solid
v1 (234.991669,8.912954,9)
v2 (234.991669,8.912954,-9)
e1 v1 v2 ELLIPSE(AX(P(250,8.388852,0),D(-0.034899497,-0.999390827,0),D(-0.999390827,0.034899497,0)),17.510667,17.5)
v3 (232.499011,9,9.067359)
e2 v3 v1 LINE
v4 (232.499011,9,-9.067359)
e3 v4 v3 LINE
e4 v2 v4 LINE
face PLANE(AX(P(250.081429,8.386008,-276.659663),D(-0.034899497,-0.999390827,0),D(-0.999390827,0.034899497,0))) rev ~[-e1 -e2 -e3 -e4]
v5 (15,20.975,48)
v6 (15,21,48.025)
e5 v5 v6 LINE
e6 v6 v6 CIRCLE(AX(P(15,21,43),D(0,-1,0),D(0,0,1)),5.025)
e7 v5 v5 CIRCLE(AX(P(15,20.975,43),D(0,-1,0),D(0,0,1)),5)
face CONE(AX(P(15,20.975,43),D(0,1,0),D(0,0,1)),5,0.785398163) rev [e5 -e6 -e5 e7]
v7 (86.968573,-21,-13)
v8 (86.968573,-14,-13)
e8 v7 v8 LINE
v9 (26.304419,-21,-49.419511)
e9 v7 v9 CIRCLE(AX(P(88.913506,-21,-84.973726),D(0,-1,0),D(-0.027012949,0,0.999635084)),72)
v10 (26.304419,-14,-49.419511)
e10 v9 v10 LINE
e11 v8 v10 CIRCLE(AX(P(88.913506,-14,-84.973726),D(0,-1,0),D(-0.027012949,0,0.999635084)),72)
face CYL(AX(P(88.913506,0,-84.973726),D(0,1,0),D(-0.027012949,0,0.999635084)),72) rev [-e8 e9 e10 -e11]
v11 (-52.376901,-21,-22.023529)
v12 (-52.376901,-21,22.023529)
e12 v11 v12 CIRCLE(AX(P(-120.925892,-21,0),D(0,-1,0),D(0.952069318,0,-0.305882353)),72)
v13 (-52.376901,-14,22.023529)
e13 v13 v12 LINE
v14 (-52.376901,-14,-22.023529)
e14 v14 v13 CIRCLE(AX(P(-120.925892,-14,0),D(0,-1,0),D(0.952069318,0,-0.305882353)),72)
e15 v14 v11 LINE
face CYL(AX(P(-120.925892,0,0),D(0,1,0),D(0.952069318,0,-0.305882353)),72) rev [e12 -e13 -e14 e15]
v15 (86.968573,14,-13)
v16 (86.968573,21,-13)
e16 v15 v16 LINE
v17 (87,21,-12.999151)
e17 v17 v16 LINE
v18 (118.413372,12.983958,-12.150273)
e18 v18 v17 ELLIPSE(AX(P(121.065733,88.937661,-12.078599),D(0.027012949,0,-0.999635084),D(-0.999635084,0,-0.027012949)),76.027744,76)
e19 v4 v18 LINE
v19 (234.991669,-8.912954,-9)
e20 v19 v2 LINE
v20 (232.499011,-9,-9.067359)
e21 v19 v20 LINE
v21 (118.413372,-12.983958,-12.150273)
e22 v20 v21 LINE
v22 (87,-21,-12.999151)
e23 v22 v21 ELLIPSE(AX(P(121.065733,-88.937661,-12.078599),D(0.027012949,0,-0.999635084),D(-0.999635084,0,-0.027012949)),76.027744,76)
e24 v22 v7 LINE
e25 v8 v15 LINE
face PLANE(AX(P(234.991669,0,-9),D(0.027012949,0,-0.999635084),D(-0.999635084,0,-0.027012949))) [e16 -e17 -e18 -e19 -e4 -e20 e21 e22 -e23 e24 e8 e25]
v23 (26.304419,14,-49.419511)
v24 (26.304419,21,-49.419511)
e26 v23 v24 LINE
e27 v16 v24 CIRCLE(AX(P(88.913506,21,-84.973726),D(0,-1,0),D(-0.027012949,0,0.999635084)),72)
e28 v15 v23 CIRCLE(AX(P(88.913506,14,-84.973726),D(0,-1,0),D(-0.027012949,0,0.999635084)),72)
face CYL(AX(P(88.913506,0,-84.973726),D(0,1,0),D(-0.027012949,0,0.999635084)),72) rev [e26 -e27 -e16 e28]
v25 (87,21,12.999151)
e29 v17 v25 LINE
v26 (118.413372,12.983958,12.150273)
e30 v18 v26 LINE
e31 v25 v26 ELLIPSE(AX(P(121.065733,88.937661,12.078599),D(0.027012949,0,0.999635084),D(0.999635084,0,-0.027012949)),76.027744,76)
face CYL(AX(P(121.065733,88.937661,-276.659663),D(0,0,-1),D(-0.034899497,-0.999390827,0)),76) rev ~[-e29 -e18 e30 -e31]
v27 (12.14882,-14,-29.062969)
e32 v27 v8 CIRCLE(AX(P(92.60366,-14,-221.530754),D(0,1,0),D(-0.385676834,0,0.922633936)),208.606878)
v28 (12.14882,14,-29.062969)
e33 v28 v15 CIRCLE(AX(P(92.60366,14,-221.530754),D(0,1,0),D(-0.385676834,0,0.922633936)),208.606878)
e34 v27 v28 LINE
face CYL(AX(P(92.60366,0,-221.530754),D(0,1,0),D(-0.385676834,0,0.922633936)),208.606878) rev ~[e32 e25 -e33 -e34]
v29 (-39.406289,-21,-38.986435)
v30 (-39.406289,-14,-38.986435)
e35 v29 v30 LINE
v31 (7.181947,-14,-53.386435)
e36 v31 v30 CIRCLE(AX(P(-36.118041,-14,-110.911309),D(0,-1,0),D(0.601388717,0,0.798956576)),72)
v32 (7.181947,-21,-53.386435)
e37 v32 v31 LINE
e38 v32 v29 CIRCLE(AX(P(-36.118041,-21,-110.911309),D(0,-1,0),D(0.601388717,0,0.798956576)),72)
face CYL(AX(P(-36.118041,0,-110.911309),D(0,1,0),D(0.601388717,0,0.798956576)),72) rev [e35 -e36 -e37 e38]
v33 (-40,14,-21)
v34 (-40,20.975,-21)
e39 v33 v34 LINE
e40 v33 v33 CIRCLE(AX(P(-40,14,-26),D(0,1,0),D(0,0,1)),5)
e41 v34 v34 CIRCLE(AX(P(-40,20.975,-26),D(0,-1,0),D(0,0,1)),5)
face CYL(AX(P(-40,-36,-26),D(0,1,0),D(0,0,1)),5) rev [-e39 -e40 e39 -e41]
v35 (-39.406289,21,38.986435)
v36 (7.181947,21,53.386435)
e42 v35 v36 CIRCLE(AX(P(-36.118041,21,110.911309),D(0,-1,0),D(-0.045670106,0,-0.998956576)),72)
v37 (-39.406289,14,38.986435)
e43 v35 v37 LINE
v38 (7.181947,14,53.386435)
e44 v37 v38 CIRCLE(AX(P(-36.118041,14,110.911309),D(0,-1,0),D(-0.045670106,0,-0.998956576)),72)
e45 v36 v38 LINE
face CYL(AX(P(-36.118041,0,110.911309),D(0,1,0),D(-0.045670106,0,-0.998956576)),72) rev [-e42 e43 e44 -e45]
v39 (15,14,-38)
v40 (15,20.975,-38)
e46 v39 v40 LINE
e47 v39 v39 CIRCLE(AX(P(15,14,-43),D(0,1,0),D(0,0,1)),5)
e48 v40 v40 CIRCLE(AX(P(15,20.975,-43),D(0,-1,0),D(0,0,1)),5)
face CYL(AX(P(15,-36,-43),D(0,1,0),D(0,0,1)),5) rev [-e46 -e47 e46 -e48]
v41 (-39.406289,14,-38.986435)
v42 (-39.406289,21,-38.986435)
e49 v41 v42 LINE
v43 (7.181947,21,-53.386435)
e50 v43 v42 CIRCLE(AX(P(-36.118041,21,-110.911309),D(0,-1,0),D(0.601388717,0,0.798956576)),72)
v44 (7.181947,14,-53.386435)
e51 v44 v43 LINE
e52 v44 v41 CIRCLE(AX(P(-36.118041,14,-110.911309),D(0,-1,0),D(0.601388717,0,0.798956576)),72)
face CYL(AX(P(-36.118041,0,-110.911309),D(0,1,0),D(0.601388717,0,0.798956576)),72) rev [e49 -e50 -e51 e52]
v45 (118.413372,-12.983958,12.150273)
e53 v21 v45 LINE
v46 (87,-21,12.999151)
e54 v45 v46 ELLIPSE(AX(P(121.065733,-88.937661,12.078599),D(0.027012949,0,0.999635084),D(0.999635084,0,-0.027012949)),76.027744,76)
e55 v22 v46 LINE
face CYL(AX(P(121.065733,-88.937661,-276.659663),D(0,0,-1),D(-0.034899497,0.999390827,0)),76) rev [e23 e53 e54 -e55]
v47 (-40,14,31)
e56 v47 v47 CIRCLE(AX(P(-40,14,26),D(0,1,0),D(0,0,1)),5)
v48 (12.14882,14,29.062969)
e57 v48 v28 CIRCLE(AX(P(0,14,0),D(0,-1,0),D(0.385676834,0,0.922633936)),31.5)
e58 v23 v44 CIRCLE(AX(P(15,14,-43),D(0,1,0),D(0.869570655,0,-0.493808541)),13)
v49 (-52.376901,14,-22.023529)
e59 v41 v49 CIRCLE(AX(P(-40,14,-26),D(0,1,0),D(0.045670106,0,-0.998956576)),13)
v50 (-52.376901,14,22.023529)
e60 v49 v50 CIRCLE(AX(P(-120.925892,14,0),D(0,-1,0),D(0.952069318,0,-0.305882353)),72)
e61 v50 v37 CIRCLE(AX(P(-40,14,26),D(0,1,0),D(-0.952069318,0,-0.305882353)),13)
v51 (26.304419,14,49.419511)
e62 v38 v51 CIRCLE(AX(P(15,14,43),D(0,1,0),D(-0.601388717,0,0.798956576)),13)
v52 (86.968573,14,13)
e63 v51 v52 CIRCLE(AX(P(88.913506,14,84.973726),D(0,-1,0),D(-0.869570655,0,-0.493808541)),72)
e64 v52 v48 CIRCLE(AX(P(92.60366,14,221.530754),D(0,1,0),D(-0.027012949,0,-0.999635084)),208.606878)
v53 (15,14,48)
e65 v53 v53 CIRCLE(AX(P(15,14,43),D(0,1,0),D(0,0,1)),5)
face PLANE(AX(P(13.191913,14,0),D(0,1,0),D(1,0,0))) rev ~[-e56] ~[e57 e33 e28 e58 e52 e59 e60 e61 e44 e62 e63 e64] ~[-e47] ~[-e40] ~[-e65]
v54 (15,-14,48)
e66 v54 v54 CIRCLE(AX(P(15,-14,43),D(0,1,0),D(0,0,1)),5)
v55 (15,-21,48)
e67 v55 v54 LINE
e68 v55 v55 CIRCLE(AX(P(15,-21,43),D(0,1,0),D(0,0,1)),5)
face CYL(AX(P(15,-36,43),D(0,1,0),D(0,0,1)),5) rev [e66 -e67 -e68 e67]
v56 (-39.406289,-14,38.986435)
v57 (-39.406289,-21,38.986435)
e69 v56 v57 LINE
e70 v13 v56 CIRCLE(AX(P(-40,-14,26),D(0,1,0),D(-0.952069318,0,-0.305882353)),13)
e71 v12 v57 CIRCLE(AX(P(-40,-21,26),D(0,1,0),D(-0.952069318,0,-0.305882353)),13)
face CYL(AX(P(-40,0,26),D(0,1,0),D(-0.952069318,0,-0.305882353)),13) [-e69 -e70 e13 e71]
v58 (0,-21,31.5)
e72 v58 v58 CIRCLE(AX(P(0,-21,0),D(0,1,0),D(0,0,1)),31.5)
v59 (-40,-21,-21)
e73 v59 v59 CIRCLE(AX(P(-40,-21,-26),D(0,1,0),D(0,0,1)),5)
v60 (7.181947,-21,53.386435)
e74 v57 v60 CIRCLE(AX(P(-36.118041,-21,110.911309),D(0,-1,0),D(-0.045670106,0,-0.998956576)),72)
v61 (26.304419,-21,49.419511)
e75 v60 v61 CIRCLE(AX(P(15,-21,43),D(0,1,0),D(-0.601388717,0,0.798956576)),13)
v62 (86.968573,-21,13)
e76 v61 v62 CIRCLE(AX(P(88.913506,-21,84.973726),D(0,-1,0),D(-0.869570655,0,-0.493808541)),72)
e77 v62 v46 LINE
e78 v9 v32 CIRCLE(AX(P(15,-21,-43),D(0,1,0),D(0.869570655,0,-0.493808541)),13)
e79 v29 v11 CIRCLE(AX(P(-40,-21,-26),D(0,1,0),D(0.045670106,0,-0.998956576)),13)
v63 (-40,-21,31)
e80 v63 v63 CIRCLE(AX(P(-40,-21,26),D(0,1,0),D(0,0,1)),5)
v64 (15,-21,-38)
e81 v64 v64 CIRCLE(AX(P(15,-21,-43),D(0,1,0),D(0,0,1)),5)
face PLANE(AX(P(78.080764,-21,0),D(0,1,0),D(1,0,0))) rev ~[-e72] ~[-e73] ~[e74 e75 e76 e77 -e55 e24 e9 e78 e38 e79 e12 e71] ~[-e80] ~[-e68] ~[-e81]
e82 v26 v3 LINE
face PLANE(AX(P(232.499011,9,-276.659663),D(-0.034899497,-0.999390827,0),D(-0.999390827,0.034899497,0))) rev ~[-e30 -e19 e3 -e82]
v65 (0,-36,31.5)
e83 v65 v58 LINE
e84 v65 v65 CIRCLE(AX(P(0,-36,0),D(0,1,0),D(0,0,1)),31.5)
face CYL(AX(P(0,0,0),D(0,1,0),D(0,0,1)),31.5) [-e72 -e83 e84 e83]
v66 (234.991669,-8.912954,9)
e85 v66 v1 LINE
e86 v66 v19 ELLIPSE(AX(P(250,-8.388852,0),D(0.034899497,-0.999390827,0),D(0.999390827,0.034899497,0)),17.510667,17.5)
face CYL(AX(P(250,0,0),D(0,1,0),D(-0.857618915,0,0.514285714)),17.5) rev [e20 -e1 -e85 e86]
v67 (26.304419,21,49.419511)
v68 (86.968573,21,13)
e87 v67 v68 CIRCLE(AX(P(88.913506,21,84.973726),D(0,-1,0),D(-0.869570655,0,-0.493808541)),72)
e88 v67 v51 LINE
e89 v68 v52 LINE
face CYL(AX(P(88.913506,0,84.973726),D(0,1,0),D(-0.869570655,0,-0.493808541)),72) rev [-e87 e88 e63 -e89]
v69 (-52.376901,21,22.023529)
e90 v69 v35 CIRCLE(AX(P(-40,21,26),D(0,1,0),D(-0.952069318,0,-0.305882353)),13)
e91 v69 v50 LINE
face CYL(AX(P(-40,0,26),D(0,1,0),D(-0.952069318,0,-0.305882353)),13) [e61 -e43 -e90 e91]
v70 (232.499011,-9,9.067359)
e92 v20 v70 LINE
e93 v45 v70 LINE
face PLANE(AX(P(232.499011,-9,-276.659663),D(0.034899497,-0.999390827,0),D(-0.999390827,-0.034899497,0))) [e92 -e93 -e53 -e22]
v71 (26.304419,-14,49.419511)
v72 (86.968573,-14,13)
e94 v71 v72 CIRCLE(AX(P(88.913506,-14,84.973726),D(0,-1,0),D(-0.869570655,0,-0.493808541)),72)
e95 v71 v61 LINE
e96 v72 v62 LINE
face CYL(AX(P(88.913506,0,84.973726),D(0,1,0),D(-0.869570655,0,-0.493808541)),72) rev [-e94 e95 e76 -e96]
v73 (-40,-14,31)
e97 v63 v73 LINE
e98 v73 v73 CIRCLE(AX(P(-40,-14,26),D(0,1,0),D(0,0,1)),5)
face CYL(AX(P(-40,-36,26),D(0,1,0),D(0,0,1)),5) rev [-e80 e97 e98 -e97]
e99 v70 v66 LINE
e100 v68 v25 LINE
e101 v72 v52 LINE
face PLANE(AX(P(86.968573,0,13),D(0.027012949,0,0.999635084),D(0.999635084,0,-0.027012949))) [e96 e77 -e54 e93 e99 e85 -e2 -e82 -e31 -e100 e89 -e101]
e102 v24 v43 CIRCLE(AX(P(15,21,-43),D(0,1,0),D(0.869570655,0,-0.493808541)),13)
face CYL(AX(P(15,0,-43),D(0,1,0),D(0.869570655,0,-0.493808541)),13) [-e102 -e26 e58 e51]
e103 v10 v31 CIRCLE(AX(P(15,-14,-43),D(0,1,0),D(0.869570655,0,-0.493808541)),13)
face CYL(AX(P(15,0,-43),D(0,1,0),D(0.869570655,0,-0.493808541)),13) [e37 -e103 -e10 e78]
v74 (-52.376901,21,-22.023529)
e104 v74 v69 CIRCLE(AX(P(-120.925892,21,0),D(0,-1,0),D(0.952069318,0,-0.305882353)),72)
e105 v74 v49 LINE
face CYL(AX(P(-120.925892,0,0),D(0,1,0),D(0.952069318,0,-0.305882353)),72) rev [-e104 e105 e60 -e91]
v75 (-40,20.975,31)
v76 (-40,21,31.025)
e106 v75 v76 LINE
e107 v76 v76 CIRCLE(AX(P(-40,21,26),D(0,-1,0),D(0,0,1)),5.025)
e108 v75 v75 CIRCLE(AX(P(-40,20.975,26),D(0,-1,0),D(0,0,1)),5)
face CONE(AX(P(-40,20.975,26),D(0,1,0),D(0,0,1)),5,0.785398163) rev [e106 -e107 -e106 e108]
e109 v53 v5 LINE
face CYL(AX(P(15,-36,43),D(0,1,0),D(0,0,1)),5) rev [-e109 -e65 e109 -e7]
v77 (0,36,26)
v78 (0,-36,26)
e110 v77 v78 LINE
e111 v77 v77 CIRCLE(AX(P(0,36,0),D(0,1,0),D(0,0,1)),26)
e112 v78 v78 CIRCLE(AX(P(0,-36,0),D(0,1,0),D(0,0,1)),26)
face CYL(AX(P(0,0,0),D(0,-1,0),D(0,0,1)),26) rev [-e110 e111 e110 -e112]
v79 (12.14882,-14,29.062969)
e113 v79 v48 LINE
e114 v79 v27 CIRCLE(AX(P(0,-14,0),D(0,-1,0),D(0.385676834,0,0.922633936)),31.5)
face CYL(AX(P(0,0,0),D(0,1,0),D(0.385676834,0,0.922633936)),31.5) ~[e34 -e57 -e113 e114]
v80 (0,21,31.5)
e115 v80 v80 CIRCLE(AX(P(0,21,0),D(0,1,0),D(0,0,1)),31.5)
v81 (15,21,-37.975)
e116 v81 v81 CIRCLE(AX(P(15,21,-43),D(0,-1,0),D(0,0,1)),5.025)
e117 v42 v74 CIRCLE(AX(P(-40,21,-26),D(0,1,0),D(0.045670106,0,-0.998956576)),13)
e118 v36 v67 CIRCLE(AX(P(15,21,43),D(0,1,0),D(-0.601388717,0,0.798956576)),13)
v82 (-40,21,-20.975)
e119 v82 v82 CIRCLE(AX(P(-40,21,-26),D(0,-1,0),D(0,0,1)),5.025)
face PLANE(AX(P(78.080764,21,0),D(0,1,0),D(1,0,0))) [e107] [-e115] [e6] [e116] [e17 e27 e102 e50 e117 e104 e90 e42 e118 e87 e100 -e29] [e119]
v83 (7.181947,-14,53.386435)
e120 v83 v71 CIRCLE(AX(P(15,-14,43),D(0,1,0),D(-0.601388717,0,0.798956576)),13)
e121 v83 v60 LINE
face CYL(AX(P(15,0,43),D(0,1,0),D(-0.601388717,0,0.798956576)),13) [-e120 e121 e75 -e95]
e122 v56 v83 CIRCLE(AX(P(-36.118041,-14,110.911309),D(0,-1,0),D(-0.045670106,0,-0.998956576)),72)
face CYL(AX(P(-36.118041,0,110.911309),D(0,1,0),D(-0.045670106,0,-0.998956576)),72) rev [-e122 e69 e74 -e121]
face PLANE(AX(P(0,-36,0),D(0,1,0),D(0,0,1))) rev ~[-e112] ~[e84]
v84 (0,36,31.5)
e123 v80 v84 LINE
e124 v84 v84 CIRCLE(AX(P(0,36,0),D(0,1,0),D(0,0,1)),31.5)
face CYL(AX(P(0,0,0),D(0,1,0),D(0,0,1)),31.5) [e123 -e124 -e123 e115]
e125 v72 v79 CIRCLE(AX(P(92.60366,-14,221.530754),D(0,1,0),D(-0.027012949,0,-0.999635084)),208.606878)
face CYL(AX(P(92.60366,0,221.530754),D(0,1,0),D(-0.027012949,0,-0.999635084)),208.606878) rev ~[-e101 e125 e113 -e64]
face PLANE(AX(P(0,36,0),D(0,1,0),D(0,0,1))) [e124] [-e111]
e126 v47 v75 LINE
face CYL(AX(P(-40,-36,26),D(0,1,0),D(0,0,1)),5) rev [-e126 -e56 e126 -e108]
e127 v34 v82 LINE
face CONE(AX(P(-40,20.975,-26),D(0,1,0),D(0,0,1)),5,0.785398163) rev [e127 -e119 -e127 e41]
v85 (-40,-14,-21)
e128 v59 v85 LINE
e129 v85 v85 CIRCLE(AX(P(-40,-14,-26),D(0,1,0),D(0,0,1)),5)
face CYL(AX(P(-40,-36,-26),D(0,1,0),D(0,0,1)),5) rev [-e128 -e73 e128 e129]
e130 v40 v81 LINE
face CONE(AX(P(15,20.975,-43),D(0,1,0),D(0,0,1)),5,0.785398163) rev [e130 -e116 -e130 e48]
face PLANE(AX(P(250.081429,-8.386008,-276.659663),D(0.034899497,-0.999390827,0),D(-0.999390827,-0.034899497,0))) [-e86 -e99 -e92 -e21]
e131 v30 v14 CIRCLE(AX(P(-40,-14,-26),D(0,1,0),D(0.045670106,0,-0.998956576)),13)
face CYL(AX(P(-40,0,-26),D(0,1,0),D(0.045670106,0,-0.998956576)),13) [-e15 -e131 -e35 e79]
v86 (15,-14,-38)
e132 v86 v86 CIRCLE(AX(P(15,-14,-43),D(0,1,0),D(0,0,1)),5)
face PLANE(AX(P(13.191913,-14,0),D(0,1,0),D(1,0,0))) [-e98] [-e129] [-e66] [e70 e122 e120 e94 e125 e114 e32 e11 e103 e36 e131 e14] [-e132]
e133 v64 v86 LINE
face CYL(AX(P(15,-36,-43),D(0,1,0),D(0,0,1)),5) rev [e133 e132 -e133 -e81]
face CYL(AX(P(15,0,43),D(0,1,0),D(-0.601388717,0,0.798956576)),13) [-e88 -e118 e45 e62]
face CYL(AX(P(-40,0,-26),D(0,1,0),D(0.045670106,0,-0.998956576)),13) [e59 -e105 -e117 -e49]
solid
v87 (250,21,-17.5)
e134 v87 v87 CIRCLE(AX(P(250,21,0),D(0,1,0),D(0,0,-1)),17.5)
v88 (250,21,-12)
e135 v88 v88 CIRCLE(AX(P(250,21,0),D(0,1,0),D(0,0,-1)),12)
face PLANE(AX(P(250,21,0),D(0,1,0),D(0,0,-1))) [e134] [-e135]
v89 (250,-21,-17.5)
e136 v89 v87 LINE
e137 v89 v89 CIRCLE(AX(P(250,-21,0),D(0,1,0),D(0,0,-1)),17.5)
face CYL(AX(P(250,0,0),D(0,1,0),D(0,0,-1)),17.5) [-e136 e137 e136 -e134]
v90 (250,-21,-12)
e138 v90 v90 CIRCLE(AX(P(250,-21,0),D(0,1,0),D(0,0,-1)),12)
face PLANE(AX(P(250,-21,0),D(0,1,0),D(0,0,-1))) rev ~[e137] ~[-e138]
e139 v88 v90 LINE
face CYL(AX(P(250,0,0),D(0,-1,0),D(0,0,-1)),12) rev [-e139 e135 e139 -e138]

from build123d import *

# Parameters (mm, degrees)
ROD_PROFILE_SKETCH_R       = 31.5
ROD_PROFILE_SKETCH_R_2     = 26
ROD_BODY_DEPTH             = 36
SKETCH2_7_R                = 31.5
BIG_END_BOSS_DEPTH         = 21
SKETCH2_8_R                = 17.5
SKETCH2_8_R_2              = 12
SMALL_END_BOSS_DEPTH       = 21
BIG_END_CUT_DEPTH          = 14
BOLT_HOLES_10_AT_2_COUNT   = 2
BOLT_HOLES_10_AT_2_PITCH   = 57.567351858
BOLT_HOLES_10_AT_3_COUNT   = 2
BOLT_HOLES_10_AT_3_PITCH   = 86
BOLT_HOLES_10_AT_4_COUNT   = 2
BOLT_HOLES_10_AT_4_PITCH   = 88.238313674
SHANK_TAPER_CUT_DEPTH      = 276.659663353
SHANK_TAPER_CUT_DEPTH_BACK = 276.659663353


with BuildPart() as part:
    # Rod Profile Sketch → Rod Body (new, symmetric)
    with BuildSketch(Plane(origin=(0, 0, 0), x_dir=(1, 0, 0), z_dir=(0, 1, 0))):
        with Locations(Location((0, 0, 0), (0, 0, 270))):
            Circle(ROD_PROFILE_SKETCH_R)
        with Locations(Location((0, 0, 0), (0, 0, 270))):
            Circle(ROD_PROFILE_SKETCH_R_2, mode=Mode.SUBTRACT)
    extrude(amount=ROD_BODY_DEPTH, both=True)

    # Sketch2_7 → Big End Boss (add, symmetric)
    with BuildSketch(Plane(origin=(0, 0, 0), x_dir=(1, 0, 0), z_dir=(0, 1, 0))):
        with BuildLine():
            Line((86.968573361, -13), (234.99166898, -9))
            ThreePointArc((234.99166898, -9), (232.5, 0), (234.99166898, 9))
            Line((234.99166898, 9), (86.968573361, 13))
            ThreePointArc((86.968573361, 13), (51.854086448, 23.24367301), (26.304418517, 49.419511039))
            ThreePointArc((26.304418517, 49.419511039), (17.6406075, 55.72899022), (7.181946677, 53.386435492))
            ThreePointArc((7.181946677, 53.386435492), (-14.855989459, 42.122318837), (-39.406288617, 38.986435492))
            ThreePointArc((-39.406288617, 38.986435492), (-50.326951915, 33.896458963), (-52.376901133, 22.023529412))
            ThreePointArc((-52.376901133, 22.023529412), (-48.925892025, 0), (-52.376901133, -22.023529412))
            ThreePointArc((-52.376901133, -22.023529412), (-50.326951915, -33.896458963), (-39.406288617, -38.986435492))
            ThreePointArc((-39.406288617, -38.986435492), (-14.855989459, -42.122318837), (7.181946677, -53.386435492))
            ThreePointArc((7.181946677, -53.386435492), (17.6406075, -55.72899022), (26.304418517, -49.419511039))
            ThreePointArc((26.304418517, -49.419511039), (51.854086448, -23.24367301), (86.968573361, -13))
        make_face()
        with Locations(Location((0, 0, 0), (0, 0, 270))):
            Circle(SKETCH2_7_R, mode=Mode.SUBTRACT)
    extrude(amount=BIG_END_BOSS_DEPTH, both=True)

    # Big End Cut Sketch → Big End Cut (cut, symmetric)
    with BuildSketch(Plane(origin=(0, 0, 0), x_dir=(1, 0, 0), z_dir=(0, 1, 0))):
        with BuildLine():
            ThreePointArc((26.304418517, -49.419511039), (51.854086448, -23.24367301), (86.968573361, -13))
            ThreePointArc((86.968573361, -13), (48.815835223, -17.5713072), (12.14882026, -29.062968986))
            ThreePointArc((12.14882026, -29.062968986), (-31.5, 0), (12.14882026, 29.062968986))
            ThreePointArc((12.14882026, 29.062968986), (48.815835223, 17.5713072), (86.968573361, 13))
            ThreePointArc((86.968573361, 13), (51.854086448, 23.24367301), (26.304418517, 49.419511039))
            ThreePointArc((26.304418517, 49.419511039), (17.6406075, 55.72899022), (7.181946677, 53.386435492))
            ThreePointArc((7.181946677, 53.386435492), (-14.855989459, 42.122318837), (-39.406288617, 38.986435492))
            ThreePointArc((-39.406288617, 38.986435492), (-50.326951915, 33.896458963), (-52.376901133, 22.023529412))
            ThreePointArc((-52.376901133, 22.023529412), (-48.925892025, 0), (-52.376901133, -22.023529412))
            ThreePointArc((-52.376901133, -22.023529412), (-50.326951915, -33.896458963), (-39.406288617, -38.986435492))
            ThreePointArc((-39.406288617, -38.986435492), (-14.855989459, -42.122318837), (7.181946677, -53.386435492))
            ThreePointArc((7.181946677, -53.386435492), (17.6406075, -55.72899022), (26.304418517, -49.419511039))
        make_face()
    extrude(amount=BIG_END_CUT_DEPTH, both=True, mode=Mode.SUBTRACT)

    # Sketch9 → Bolt Holes _10 (revolve, cut)
    with BuildSketch(Plane(origin=(15, 21, -43), x_dir=(0, 0, 1), z_dir=(1, 0, 0))):
        Polygon((0, 0), (0, 57), (5, 57), (5, 0.025), (5.025, 0), align=None)
    bolt_holes_10 = revolve(axis=Axis((15, 27.35, -43), (0, -1, 0)), mode=Mode.SUBTRACT)

    # Bolt Holes _10 at 2: Bolt Holes _10 ×2
    with Locations(*[Vector(-0.9554026409829016, 0, 0.29530627084926053) * (i * BOLT_HOLES_10_AT_2_PITCH) for i in range(1, BOLT_HOLES_10_AT_2_COUNT)]):
        add(bolt_holes_10, mode=Mode.SUBTRACT)

    # Bolt Holes _10 at 3: Bolt Holes _10 ×2
    with Locations(*[(0, 0, i * BOLT_HOLES_10_AT_3_PITCH) for i in range(1, BOLT_HOLES_10_AT_3_COUNT)]):
        add(bolt_holes_10, mode=Mode.SUBTRACT)

    # Bolt Holes _10 at 4: Bolt Holes _10 ×2
    with Locations(*[Vector(-0.623312002576454, 0, 0.7819732395959151) * (i * BOLT_HOLES_10_AT_4_PITCH) for i in range(1, BOLT_HOLES_10_AT_4_COUNT)]):
        add(bolt_holes_10, mode=Mode.SUBTRACT)

    # Shank Taper Sketch → Shank Taper Cut (cut, two sides: drawn at the far end of the back side and taken through both)
    with BuildSketch(Plane.XY.offset(-SHANK_TAPER_CUT_DEPTH_BACK)):
        with BuildLine():
            Line((232.499010748, 9), (118.413371717, 12.983958303))
            ThreePointArc((118.413371717, 12.983958303), (102.27427636, 15.297447008), (87, 21))
            Line((87, 21), (232.499010748, 21))
            Line((232.499010748, 21), (250.081428832, 21))
            Line((250.081428832, 21), (250.081428832, 8.386008431))
            Line((250.081428832, 8.386008431), (232.499010748, 9))
        make_face()
        with BuildLine():
            Line((232.499010748, -21), (250.081428832, -21))
            Line((250.081428832, -21), (250.081428832, -8.386008431))
            Line((250.081428832, -8.386008431), (232.499010748, -9))
            Line((232.499010748, -9), (118.413371717, -12.983958303))
            ThreePointArc((118.413371717, -12.983958303), (102.27427636, -15.297447008), (87, -21))
            Line((87, -21), (232.499010748, -21))
        make_face()
    extrude(amount=SHANK_TAPER_CUT_DEPTH + SHANK_TAPER_CUT_DEPTH_BACK, mode=Mode.SUBTRACT)


with BuildPart() as body_2:
    # Sketch2_8 → Small End Boss (new, symmetric)
    with BuildSketch(Plane(origin=(0, 0, 0), x_dir=(1, 0, 0), z_dir=(0, 1, 0))):
        with Locations(Location((250, 0, 0), (0, 0, 90))):
            Circle(SKETCH2_8_R)
        with Locations(Location((250, 0, 0), (0, 0, 90))):
            Circle(SKETCH2_8_R_2, mode=Mode.SUBTRACT)
    extrude(amount=SMALL_END_BOSS_DEPTH, both=True)


solid = Compound([part.part, body_2.part])
